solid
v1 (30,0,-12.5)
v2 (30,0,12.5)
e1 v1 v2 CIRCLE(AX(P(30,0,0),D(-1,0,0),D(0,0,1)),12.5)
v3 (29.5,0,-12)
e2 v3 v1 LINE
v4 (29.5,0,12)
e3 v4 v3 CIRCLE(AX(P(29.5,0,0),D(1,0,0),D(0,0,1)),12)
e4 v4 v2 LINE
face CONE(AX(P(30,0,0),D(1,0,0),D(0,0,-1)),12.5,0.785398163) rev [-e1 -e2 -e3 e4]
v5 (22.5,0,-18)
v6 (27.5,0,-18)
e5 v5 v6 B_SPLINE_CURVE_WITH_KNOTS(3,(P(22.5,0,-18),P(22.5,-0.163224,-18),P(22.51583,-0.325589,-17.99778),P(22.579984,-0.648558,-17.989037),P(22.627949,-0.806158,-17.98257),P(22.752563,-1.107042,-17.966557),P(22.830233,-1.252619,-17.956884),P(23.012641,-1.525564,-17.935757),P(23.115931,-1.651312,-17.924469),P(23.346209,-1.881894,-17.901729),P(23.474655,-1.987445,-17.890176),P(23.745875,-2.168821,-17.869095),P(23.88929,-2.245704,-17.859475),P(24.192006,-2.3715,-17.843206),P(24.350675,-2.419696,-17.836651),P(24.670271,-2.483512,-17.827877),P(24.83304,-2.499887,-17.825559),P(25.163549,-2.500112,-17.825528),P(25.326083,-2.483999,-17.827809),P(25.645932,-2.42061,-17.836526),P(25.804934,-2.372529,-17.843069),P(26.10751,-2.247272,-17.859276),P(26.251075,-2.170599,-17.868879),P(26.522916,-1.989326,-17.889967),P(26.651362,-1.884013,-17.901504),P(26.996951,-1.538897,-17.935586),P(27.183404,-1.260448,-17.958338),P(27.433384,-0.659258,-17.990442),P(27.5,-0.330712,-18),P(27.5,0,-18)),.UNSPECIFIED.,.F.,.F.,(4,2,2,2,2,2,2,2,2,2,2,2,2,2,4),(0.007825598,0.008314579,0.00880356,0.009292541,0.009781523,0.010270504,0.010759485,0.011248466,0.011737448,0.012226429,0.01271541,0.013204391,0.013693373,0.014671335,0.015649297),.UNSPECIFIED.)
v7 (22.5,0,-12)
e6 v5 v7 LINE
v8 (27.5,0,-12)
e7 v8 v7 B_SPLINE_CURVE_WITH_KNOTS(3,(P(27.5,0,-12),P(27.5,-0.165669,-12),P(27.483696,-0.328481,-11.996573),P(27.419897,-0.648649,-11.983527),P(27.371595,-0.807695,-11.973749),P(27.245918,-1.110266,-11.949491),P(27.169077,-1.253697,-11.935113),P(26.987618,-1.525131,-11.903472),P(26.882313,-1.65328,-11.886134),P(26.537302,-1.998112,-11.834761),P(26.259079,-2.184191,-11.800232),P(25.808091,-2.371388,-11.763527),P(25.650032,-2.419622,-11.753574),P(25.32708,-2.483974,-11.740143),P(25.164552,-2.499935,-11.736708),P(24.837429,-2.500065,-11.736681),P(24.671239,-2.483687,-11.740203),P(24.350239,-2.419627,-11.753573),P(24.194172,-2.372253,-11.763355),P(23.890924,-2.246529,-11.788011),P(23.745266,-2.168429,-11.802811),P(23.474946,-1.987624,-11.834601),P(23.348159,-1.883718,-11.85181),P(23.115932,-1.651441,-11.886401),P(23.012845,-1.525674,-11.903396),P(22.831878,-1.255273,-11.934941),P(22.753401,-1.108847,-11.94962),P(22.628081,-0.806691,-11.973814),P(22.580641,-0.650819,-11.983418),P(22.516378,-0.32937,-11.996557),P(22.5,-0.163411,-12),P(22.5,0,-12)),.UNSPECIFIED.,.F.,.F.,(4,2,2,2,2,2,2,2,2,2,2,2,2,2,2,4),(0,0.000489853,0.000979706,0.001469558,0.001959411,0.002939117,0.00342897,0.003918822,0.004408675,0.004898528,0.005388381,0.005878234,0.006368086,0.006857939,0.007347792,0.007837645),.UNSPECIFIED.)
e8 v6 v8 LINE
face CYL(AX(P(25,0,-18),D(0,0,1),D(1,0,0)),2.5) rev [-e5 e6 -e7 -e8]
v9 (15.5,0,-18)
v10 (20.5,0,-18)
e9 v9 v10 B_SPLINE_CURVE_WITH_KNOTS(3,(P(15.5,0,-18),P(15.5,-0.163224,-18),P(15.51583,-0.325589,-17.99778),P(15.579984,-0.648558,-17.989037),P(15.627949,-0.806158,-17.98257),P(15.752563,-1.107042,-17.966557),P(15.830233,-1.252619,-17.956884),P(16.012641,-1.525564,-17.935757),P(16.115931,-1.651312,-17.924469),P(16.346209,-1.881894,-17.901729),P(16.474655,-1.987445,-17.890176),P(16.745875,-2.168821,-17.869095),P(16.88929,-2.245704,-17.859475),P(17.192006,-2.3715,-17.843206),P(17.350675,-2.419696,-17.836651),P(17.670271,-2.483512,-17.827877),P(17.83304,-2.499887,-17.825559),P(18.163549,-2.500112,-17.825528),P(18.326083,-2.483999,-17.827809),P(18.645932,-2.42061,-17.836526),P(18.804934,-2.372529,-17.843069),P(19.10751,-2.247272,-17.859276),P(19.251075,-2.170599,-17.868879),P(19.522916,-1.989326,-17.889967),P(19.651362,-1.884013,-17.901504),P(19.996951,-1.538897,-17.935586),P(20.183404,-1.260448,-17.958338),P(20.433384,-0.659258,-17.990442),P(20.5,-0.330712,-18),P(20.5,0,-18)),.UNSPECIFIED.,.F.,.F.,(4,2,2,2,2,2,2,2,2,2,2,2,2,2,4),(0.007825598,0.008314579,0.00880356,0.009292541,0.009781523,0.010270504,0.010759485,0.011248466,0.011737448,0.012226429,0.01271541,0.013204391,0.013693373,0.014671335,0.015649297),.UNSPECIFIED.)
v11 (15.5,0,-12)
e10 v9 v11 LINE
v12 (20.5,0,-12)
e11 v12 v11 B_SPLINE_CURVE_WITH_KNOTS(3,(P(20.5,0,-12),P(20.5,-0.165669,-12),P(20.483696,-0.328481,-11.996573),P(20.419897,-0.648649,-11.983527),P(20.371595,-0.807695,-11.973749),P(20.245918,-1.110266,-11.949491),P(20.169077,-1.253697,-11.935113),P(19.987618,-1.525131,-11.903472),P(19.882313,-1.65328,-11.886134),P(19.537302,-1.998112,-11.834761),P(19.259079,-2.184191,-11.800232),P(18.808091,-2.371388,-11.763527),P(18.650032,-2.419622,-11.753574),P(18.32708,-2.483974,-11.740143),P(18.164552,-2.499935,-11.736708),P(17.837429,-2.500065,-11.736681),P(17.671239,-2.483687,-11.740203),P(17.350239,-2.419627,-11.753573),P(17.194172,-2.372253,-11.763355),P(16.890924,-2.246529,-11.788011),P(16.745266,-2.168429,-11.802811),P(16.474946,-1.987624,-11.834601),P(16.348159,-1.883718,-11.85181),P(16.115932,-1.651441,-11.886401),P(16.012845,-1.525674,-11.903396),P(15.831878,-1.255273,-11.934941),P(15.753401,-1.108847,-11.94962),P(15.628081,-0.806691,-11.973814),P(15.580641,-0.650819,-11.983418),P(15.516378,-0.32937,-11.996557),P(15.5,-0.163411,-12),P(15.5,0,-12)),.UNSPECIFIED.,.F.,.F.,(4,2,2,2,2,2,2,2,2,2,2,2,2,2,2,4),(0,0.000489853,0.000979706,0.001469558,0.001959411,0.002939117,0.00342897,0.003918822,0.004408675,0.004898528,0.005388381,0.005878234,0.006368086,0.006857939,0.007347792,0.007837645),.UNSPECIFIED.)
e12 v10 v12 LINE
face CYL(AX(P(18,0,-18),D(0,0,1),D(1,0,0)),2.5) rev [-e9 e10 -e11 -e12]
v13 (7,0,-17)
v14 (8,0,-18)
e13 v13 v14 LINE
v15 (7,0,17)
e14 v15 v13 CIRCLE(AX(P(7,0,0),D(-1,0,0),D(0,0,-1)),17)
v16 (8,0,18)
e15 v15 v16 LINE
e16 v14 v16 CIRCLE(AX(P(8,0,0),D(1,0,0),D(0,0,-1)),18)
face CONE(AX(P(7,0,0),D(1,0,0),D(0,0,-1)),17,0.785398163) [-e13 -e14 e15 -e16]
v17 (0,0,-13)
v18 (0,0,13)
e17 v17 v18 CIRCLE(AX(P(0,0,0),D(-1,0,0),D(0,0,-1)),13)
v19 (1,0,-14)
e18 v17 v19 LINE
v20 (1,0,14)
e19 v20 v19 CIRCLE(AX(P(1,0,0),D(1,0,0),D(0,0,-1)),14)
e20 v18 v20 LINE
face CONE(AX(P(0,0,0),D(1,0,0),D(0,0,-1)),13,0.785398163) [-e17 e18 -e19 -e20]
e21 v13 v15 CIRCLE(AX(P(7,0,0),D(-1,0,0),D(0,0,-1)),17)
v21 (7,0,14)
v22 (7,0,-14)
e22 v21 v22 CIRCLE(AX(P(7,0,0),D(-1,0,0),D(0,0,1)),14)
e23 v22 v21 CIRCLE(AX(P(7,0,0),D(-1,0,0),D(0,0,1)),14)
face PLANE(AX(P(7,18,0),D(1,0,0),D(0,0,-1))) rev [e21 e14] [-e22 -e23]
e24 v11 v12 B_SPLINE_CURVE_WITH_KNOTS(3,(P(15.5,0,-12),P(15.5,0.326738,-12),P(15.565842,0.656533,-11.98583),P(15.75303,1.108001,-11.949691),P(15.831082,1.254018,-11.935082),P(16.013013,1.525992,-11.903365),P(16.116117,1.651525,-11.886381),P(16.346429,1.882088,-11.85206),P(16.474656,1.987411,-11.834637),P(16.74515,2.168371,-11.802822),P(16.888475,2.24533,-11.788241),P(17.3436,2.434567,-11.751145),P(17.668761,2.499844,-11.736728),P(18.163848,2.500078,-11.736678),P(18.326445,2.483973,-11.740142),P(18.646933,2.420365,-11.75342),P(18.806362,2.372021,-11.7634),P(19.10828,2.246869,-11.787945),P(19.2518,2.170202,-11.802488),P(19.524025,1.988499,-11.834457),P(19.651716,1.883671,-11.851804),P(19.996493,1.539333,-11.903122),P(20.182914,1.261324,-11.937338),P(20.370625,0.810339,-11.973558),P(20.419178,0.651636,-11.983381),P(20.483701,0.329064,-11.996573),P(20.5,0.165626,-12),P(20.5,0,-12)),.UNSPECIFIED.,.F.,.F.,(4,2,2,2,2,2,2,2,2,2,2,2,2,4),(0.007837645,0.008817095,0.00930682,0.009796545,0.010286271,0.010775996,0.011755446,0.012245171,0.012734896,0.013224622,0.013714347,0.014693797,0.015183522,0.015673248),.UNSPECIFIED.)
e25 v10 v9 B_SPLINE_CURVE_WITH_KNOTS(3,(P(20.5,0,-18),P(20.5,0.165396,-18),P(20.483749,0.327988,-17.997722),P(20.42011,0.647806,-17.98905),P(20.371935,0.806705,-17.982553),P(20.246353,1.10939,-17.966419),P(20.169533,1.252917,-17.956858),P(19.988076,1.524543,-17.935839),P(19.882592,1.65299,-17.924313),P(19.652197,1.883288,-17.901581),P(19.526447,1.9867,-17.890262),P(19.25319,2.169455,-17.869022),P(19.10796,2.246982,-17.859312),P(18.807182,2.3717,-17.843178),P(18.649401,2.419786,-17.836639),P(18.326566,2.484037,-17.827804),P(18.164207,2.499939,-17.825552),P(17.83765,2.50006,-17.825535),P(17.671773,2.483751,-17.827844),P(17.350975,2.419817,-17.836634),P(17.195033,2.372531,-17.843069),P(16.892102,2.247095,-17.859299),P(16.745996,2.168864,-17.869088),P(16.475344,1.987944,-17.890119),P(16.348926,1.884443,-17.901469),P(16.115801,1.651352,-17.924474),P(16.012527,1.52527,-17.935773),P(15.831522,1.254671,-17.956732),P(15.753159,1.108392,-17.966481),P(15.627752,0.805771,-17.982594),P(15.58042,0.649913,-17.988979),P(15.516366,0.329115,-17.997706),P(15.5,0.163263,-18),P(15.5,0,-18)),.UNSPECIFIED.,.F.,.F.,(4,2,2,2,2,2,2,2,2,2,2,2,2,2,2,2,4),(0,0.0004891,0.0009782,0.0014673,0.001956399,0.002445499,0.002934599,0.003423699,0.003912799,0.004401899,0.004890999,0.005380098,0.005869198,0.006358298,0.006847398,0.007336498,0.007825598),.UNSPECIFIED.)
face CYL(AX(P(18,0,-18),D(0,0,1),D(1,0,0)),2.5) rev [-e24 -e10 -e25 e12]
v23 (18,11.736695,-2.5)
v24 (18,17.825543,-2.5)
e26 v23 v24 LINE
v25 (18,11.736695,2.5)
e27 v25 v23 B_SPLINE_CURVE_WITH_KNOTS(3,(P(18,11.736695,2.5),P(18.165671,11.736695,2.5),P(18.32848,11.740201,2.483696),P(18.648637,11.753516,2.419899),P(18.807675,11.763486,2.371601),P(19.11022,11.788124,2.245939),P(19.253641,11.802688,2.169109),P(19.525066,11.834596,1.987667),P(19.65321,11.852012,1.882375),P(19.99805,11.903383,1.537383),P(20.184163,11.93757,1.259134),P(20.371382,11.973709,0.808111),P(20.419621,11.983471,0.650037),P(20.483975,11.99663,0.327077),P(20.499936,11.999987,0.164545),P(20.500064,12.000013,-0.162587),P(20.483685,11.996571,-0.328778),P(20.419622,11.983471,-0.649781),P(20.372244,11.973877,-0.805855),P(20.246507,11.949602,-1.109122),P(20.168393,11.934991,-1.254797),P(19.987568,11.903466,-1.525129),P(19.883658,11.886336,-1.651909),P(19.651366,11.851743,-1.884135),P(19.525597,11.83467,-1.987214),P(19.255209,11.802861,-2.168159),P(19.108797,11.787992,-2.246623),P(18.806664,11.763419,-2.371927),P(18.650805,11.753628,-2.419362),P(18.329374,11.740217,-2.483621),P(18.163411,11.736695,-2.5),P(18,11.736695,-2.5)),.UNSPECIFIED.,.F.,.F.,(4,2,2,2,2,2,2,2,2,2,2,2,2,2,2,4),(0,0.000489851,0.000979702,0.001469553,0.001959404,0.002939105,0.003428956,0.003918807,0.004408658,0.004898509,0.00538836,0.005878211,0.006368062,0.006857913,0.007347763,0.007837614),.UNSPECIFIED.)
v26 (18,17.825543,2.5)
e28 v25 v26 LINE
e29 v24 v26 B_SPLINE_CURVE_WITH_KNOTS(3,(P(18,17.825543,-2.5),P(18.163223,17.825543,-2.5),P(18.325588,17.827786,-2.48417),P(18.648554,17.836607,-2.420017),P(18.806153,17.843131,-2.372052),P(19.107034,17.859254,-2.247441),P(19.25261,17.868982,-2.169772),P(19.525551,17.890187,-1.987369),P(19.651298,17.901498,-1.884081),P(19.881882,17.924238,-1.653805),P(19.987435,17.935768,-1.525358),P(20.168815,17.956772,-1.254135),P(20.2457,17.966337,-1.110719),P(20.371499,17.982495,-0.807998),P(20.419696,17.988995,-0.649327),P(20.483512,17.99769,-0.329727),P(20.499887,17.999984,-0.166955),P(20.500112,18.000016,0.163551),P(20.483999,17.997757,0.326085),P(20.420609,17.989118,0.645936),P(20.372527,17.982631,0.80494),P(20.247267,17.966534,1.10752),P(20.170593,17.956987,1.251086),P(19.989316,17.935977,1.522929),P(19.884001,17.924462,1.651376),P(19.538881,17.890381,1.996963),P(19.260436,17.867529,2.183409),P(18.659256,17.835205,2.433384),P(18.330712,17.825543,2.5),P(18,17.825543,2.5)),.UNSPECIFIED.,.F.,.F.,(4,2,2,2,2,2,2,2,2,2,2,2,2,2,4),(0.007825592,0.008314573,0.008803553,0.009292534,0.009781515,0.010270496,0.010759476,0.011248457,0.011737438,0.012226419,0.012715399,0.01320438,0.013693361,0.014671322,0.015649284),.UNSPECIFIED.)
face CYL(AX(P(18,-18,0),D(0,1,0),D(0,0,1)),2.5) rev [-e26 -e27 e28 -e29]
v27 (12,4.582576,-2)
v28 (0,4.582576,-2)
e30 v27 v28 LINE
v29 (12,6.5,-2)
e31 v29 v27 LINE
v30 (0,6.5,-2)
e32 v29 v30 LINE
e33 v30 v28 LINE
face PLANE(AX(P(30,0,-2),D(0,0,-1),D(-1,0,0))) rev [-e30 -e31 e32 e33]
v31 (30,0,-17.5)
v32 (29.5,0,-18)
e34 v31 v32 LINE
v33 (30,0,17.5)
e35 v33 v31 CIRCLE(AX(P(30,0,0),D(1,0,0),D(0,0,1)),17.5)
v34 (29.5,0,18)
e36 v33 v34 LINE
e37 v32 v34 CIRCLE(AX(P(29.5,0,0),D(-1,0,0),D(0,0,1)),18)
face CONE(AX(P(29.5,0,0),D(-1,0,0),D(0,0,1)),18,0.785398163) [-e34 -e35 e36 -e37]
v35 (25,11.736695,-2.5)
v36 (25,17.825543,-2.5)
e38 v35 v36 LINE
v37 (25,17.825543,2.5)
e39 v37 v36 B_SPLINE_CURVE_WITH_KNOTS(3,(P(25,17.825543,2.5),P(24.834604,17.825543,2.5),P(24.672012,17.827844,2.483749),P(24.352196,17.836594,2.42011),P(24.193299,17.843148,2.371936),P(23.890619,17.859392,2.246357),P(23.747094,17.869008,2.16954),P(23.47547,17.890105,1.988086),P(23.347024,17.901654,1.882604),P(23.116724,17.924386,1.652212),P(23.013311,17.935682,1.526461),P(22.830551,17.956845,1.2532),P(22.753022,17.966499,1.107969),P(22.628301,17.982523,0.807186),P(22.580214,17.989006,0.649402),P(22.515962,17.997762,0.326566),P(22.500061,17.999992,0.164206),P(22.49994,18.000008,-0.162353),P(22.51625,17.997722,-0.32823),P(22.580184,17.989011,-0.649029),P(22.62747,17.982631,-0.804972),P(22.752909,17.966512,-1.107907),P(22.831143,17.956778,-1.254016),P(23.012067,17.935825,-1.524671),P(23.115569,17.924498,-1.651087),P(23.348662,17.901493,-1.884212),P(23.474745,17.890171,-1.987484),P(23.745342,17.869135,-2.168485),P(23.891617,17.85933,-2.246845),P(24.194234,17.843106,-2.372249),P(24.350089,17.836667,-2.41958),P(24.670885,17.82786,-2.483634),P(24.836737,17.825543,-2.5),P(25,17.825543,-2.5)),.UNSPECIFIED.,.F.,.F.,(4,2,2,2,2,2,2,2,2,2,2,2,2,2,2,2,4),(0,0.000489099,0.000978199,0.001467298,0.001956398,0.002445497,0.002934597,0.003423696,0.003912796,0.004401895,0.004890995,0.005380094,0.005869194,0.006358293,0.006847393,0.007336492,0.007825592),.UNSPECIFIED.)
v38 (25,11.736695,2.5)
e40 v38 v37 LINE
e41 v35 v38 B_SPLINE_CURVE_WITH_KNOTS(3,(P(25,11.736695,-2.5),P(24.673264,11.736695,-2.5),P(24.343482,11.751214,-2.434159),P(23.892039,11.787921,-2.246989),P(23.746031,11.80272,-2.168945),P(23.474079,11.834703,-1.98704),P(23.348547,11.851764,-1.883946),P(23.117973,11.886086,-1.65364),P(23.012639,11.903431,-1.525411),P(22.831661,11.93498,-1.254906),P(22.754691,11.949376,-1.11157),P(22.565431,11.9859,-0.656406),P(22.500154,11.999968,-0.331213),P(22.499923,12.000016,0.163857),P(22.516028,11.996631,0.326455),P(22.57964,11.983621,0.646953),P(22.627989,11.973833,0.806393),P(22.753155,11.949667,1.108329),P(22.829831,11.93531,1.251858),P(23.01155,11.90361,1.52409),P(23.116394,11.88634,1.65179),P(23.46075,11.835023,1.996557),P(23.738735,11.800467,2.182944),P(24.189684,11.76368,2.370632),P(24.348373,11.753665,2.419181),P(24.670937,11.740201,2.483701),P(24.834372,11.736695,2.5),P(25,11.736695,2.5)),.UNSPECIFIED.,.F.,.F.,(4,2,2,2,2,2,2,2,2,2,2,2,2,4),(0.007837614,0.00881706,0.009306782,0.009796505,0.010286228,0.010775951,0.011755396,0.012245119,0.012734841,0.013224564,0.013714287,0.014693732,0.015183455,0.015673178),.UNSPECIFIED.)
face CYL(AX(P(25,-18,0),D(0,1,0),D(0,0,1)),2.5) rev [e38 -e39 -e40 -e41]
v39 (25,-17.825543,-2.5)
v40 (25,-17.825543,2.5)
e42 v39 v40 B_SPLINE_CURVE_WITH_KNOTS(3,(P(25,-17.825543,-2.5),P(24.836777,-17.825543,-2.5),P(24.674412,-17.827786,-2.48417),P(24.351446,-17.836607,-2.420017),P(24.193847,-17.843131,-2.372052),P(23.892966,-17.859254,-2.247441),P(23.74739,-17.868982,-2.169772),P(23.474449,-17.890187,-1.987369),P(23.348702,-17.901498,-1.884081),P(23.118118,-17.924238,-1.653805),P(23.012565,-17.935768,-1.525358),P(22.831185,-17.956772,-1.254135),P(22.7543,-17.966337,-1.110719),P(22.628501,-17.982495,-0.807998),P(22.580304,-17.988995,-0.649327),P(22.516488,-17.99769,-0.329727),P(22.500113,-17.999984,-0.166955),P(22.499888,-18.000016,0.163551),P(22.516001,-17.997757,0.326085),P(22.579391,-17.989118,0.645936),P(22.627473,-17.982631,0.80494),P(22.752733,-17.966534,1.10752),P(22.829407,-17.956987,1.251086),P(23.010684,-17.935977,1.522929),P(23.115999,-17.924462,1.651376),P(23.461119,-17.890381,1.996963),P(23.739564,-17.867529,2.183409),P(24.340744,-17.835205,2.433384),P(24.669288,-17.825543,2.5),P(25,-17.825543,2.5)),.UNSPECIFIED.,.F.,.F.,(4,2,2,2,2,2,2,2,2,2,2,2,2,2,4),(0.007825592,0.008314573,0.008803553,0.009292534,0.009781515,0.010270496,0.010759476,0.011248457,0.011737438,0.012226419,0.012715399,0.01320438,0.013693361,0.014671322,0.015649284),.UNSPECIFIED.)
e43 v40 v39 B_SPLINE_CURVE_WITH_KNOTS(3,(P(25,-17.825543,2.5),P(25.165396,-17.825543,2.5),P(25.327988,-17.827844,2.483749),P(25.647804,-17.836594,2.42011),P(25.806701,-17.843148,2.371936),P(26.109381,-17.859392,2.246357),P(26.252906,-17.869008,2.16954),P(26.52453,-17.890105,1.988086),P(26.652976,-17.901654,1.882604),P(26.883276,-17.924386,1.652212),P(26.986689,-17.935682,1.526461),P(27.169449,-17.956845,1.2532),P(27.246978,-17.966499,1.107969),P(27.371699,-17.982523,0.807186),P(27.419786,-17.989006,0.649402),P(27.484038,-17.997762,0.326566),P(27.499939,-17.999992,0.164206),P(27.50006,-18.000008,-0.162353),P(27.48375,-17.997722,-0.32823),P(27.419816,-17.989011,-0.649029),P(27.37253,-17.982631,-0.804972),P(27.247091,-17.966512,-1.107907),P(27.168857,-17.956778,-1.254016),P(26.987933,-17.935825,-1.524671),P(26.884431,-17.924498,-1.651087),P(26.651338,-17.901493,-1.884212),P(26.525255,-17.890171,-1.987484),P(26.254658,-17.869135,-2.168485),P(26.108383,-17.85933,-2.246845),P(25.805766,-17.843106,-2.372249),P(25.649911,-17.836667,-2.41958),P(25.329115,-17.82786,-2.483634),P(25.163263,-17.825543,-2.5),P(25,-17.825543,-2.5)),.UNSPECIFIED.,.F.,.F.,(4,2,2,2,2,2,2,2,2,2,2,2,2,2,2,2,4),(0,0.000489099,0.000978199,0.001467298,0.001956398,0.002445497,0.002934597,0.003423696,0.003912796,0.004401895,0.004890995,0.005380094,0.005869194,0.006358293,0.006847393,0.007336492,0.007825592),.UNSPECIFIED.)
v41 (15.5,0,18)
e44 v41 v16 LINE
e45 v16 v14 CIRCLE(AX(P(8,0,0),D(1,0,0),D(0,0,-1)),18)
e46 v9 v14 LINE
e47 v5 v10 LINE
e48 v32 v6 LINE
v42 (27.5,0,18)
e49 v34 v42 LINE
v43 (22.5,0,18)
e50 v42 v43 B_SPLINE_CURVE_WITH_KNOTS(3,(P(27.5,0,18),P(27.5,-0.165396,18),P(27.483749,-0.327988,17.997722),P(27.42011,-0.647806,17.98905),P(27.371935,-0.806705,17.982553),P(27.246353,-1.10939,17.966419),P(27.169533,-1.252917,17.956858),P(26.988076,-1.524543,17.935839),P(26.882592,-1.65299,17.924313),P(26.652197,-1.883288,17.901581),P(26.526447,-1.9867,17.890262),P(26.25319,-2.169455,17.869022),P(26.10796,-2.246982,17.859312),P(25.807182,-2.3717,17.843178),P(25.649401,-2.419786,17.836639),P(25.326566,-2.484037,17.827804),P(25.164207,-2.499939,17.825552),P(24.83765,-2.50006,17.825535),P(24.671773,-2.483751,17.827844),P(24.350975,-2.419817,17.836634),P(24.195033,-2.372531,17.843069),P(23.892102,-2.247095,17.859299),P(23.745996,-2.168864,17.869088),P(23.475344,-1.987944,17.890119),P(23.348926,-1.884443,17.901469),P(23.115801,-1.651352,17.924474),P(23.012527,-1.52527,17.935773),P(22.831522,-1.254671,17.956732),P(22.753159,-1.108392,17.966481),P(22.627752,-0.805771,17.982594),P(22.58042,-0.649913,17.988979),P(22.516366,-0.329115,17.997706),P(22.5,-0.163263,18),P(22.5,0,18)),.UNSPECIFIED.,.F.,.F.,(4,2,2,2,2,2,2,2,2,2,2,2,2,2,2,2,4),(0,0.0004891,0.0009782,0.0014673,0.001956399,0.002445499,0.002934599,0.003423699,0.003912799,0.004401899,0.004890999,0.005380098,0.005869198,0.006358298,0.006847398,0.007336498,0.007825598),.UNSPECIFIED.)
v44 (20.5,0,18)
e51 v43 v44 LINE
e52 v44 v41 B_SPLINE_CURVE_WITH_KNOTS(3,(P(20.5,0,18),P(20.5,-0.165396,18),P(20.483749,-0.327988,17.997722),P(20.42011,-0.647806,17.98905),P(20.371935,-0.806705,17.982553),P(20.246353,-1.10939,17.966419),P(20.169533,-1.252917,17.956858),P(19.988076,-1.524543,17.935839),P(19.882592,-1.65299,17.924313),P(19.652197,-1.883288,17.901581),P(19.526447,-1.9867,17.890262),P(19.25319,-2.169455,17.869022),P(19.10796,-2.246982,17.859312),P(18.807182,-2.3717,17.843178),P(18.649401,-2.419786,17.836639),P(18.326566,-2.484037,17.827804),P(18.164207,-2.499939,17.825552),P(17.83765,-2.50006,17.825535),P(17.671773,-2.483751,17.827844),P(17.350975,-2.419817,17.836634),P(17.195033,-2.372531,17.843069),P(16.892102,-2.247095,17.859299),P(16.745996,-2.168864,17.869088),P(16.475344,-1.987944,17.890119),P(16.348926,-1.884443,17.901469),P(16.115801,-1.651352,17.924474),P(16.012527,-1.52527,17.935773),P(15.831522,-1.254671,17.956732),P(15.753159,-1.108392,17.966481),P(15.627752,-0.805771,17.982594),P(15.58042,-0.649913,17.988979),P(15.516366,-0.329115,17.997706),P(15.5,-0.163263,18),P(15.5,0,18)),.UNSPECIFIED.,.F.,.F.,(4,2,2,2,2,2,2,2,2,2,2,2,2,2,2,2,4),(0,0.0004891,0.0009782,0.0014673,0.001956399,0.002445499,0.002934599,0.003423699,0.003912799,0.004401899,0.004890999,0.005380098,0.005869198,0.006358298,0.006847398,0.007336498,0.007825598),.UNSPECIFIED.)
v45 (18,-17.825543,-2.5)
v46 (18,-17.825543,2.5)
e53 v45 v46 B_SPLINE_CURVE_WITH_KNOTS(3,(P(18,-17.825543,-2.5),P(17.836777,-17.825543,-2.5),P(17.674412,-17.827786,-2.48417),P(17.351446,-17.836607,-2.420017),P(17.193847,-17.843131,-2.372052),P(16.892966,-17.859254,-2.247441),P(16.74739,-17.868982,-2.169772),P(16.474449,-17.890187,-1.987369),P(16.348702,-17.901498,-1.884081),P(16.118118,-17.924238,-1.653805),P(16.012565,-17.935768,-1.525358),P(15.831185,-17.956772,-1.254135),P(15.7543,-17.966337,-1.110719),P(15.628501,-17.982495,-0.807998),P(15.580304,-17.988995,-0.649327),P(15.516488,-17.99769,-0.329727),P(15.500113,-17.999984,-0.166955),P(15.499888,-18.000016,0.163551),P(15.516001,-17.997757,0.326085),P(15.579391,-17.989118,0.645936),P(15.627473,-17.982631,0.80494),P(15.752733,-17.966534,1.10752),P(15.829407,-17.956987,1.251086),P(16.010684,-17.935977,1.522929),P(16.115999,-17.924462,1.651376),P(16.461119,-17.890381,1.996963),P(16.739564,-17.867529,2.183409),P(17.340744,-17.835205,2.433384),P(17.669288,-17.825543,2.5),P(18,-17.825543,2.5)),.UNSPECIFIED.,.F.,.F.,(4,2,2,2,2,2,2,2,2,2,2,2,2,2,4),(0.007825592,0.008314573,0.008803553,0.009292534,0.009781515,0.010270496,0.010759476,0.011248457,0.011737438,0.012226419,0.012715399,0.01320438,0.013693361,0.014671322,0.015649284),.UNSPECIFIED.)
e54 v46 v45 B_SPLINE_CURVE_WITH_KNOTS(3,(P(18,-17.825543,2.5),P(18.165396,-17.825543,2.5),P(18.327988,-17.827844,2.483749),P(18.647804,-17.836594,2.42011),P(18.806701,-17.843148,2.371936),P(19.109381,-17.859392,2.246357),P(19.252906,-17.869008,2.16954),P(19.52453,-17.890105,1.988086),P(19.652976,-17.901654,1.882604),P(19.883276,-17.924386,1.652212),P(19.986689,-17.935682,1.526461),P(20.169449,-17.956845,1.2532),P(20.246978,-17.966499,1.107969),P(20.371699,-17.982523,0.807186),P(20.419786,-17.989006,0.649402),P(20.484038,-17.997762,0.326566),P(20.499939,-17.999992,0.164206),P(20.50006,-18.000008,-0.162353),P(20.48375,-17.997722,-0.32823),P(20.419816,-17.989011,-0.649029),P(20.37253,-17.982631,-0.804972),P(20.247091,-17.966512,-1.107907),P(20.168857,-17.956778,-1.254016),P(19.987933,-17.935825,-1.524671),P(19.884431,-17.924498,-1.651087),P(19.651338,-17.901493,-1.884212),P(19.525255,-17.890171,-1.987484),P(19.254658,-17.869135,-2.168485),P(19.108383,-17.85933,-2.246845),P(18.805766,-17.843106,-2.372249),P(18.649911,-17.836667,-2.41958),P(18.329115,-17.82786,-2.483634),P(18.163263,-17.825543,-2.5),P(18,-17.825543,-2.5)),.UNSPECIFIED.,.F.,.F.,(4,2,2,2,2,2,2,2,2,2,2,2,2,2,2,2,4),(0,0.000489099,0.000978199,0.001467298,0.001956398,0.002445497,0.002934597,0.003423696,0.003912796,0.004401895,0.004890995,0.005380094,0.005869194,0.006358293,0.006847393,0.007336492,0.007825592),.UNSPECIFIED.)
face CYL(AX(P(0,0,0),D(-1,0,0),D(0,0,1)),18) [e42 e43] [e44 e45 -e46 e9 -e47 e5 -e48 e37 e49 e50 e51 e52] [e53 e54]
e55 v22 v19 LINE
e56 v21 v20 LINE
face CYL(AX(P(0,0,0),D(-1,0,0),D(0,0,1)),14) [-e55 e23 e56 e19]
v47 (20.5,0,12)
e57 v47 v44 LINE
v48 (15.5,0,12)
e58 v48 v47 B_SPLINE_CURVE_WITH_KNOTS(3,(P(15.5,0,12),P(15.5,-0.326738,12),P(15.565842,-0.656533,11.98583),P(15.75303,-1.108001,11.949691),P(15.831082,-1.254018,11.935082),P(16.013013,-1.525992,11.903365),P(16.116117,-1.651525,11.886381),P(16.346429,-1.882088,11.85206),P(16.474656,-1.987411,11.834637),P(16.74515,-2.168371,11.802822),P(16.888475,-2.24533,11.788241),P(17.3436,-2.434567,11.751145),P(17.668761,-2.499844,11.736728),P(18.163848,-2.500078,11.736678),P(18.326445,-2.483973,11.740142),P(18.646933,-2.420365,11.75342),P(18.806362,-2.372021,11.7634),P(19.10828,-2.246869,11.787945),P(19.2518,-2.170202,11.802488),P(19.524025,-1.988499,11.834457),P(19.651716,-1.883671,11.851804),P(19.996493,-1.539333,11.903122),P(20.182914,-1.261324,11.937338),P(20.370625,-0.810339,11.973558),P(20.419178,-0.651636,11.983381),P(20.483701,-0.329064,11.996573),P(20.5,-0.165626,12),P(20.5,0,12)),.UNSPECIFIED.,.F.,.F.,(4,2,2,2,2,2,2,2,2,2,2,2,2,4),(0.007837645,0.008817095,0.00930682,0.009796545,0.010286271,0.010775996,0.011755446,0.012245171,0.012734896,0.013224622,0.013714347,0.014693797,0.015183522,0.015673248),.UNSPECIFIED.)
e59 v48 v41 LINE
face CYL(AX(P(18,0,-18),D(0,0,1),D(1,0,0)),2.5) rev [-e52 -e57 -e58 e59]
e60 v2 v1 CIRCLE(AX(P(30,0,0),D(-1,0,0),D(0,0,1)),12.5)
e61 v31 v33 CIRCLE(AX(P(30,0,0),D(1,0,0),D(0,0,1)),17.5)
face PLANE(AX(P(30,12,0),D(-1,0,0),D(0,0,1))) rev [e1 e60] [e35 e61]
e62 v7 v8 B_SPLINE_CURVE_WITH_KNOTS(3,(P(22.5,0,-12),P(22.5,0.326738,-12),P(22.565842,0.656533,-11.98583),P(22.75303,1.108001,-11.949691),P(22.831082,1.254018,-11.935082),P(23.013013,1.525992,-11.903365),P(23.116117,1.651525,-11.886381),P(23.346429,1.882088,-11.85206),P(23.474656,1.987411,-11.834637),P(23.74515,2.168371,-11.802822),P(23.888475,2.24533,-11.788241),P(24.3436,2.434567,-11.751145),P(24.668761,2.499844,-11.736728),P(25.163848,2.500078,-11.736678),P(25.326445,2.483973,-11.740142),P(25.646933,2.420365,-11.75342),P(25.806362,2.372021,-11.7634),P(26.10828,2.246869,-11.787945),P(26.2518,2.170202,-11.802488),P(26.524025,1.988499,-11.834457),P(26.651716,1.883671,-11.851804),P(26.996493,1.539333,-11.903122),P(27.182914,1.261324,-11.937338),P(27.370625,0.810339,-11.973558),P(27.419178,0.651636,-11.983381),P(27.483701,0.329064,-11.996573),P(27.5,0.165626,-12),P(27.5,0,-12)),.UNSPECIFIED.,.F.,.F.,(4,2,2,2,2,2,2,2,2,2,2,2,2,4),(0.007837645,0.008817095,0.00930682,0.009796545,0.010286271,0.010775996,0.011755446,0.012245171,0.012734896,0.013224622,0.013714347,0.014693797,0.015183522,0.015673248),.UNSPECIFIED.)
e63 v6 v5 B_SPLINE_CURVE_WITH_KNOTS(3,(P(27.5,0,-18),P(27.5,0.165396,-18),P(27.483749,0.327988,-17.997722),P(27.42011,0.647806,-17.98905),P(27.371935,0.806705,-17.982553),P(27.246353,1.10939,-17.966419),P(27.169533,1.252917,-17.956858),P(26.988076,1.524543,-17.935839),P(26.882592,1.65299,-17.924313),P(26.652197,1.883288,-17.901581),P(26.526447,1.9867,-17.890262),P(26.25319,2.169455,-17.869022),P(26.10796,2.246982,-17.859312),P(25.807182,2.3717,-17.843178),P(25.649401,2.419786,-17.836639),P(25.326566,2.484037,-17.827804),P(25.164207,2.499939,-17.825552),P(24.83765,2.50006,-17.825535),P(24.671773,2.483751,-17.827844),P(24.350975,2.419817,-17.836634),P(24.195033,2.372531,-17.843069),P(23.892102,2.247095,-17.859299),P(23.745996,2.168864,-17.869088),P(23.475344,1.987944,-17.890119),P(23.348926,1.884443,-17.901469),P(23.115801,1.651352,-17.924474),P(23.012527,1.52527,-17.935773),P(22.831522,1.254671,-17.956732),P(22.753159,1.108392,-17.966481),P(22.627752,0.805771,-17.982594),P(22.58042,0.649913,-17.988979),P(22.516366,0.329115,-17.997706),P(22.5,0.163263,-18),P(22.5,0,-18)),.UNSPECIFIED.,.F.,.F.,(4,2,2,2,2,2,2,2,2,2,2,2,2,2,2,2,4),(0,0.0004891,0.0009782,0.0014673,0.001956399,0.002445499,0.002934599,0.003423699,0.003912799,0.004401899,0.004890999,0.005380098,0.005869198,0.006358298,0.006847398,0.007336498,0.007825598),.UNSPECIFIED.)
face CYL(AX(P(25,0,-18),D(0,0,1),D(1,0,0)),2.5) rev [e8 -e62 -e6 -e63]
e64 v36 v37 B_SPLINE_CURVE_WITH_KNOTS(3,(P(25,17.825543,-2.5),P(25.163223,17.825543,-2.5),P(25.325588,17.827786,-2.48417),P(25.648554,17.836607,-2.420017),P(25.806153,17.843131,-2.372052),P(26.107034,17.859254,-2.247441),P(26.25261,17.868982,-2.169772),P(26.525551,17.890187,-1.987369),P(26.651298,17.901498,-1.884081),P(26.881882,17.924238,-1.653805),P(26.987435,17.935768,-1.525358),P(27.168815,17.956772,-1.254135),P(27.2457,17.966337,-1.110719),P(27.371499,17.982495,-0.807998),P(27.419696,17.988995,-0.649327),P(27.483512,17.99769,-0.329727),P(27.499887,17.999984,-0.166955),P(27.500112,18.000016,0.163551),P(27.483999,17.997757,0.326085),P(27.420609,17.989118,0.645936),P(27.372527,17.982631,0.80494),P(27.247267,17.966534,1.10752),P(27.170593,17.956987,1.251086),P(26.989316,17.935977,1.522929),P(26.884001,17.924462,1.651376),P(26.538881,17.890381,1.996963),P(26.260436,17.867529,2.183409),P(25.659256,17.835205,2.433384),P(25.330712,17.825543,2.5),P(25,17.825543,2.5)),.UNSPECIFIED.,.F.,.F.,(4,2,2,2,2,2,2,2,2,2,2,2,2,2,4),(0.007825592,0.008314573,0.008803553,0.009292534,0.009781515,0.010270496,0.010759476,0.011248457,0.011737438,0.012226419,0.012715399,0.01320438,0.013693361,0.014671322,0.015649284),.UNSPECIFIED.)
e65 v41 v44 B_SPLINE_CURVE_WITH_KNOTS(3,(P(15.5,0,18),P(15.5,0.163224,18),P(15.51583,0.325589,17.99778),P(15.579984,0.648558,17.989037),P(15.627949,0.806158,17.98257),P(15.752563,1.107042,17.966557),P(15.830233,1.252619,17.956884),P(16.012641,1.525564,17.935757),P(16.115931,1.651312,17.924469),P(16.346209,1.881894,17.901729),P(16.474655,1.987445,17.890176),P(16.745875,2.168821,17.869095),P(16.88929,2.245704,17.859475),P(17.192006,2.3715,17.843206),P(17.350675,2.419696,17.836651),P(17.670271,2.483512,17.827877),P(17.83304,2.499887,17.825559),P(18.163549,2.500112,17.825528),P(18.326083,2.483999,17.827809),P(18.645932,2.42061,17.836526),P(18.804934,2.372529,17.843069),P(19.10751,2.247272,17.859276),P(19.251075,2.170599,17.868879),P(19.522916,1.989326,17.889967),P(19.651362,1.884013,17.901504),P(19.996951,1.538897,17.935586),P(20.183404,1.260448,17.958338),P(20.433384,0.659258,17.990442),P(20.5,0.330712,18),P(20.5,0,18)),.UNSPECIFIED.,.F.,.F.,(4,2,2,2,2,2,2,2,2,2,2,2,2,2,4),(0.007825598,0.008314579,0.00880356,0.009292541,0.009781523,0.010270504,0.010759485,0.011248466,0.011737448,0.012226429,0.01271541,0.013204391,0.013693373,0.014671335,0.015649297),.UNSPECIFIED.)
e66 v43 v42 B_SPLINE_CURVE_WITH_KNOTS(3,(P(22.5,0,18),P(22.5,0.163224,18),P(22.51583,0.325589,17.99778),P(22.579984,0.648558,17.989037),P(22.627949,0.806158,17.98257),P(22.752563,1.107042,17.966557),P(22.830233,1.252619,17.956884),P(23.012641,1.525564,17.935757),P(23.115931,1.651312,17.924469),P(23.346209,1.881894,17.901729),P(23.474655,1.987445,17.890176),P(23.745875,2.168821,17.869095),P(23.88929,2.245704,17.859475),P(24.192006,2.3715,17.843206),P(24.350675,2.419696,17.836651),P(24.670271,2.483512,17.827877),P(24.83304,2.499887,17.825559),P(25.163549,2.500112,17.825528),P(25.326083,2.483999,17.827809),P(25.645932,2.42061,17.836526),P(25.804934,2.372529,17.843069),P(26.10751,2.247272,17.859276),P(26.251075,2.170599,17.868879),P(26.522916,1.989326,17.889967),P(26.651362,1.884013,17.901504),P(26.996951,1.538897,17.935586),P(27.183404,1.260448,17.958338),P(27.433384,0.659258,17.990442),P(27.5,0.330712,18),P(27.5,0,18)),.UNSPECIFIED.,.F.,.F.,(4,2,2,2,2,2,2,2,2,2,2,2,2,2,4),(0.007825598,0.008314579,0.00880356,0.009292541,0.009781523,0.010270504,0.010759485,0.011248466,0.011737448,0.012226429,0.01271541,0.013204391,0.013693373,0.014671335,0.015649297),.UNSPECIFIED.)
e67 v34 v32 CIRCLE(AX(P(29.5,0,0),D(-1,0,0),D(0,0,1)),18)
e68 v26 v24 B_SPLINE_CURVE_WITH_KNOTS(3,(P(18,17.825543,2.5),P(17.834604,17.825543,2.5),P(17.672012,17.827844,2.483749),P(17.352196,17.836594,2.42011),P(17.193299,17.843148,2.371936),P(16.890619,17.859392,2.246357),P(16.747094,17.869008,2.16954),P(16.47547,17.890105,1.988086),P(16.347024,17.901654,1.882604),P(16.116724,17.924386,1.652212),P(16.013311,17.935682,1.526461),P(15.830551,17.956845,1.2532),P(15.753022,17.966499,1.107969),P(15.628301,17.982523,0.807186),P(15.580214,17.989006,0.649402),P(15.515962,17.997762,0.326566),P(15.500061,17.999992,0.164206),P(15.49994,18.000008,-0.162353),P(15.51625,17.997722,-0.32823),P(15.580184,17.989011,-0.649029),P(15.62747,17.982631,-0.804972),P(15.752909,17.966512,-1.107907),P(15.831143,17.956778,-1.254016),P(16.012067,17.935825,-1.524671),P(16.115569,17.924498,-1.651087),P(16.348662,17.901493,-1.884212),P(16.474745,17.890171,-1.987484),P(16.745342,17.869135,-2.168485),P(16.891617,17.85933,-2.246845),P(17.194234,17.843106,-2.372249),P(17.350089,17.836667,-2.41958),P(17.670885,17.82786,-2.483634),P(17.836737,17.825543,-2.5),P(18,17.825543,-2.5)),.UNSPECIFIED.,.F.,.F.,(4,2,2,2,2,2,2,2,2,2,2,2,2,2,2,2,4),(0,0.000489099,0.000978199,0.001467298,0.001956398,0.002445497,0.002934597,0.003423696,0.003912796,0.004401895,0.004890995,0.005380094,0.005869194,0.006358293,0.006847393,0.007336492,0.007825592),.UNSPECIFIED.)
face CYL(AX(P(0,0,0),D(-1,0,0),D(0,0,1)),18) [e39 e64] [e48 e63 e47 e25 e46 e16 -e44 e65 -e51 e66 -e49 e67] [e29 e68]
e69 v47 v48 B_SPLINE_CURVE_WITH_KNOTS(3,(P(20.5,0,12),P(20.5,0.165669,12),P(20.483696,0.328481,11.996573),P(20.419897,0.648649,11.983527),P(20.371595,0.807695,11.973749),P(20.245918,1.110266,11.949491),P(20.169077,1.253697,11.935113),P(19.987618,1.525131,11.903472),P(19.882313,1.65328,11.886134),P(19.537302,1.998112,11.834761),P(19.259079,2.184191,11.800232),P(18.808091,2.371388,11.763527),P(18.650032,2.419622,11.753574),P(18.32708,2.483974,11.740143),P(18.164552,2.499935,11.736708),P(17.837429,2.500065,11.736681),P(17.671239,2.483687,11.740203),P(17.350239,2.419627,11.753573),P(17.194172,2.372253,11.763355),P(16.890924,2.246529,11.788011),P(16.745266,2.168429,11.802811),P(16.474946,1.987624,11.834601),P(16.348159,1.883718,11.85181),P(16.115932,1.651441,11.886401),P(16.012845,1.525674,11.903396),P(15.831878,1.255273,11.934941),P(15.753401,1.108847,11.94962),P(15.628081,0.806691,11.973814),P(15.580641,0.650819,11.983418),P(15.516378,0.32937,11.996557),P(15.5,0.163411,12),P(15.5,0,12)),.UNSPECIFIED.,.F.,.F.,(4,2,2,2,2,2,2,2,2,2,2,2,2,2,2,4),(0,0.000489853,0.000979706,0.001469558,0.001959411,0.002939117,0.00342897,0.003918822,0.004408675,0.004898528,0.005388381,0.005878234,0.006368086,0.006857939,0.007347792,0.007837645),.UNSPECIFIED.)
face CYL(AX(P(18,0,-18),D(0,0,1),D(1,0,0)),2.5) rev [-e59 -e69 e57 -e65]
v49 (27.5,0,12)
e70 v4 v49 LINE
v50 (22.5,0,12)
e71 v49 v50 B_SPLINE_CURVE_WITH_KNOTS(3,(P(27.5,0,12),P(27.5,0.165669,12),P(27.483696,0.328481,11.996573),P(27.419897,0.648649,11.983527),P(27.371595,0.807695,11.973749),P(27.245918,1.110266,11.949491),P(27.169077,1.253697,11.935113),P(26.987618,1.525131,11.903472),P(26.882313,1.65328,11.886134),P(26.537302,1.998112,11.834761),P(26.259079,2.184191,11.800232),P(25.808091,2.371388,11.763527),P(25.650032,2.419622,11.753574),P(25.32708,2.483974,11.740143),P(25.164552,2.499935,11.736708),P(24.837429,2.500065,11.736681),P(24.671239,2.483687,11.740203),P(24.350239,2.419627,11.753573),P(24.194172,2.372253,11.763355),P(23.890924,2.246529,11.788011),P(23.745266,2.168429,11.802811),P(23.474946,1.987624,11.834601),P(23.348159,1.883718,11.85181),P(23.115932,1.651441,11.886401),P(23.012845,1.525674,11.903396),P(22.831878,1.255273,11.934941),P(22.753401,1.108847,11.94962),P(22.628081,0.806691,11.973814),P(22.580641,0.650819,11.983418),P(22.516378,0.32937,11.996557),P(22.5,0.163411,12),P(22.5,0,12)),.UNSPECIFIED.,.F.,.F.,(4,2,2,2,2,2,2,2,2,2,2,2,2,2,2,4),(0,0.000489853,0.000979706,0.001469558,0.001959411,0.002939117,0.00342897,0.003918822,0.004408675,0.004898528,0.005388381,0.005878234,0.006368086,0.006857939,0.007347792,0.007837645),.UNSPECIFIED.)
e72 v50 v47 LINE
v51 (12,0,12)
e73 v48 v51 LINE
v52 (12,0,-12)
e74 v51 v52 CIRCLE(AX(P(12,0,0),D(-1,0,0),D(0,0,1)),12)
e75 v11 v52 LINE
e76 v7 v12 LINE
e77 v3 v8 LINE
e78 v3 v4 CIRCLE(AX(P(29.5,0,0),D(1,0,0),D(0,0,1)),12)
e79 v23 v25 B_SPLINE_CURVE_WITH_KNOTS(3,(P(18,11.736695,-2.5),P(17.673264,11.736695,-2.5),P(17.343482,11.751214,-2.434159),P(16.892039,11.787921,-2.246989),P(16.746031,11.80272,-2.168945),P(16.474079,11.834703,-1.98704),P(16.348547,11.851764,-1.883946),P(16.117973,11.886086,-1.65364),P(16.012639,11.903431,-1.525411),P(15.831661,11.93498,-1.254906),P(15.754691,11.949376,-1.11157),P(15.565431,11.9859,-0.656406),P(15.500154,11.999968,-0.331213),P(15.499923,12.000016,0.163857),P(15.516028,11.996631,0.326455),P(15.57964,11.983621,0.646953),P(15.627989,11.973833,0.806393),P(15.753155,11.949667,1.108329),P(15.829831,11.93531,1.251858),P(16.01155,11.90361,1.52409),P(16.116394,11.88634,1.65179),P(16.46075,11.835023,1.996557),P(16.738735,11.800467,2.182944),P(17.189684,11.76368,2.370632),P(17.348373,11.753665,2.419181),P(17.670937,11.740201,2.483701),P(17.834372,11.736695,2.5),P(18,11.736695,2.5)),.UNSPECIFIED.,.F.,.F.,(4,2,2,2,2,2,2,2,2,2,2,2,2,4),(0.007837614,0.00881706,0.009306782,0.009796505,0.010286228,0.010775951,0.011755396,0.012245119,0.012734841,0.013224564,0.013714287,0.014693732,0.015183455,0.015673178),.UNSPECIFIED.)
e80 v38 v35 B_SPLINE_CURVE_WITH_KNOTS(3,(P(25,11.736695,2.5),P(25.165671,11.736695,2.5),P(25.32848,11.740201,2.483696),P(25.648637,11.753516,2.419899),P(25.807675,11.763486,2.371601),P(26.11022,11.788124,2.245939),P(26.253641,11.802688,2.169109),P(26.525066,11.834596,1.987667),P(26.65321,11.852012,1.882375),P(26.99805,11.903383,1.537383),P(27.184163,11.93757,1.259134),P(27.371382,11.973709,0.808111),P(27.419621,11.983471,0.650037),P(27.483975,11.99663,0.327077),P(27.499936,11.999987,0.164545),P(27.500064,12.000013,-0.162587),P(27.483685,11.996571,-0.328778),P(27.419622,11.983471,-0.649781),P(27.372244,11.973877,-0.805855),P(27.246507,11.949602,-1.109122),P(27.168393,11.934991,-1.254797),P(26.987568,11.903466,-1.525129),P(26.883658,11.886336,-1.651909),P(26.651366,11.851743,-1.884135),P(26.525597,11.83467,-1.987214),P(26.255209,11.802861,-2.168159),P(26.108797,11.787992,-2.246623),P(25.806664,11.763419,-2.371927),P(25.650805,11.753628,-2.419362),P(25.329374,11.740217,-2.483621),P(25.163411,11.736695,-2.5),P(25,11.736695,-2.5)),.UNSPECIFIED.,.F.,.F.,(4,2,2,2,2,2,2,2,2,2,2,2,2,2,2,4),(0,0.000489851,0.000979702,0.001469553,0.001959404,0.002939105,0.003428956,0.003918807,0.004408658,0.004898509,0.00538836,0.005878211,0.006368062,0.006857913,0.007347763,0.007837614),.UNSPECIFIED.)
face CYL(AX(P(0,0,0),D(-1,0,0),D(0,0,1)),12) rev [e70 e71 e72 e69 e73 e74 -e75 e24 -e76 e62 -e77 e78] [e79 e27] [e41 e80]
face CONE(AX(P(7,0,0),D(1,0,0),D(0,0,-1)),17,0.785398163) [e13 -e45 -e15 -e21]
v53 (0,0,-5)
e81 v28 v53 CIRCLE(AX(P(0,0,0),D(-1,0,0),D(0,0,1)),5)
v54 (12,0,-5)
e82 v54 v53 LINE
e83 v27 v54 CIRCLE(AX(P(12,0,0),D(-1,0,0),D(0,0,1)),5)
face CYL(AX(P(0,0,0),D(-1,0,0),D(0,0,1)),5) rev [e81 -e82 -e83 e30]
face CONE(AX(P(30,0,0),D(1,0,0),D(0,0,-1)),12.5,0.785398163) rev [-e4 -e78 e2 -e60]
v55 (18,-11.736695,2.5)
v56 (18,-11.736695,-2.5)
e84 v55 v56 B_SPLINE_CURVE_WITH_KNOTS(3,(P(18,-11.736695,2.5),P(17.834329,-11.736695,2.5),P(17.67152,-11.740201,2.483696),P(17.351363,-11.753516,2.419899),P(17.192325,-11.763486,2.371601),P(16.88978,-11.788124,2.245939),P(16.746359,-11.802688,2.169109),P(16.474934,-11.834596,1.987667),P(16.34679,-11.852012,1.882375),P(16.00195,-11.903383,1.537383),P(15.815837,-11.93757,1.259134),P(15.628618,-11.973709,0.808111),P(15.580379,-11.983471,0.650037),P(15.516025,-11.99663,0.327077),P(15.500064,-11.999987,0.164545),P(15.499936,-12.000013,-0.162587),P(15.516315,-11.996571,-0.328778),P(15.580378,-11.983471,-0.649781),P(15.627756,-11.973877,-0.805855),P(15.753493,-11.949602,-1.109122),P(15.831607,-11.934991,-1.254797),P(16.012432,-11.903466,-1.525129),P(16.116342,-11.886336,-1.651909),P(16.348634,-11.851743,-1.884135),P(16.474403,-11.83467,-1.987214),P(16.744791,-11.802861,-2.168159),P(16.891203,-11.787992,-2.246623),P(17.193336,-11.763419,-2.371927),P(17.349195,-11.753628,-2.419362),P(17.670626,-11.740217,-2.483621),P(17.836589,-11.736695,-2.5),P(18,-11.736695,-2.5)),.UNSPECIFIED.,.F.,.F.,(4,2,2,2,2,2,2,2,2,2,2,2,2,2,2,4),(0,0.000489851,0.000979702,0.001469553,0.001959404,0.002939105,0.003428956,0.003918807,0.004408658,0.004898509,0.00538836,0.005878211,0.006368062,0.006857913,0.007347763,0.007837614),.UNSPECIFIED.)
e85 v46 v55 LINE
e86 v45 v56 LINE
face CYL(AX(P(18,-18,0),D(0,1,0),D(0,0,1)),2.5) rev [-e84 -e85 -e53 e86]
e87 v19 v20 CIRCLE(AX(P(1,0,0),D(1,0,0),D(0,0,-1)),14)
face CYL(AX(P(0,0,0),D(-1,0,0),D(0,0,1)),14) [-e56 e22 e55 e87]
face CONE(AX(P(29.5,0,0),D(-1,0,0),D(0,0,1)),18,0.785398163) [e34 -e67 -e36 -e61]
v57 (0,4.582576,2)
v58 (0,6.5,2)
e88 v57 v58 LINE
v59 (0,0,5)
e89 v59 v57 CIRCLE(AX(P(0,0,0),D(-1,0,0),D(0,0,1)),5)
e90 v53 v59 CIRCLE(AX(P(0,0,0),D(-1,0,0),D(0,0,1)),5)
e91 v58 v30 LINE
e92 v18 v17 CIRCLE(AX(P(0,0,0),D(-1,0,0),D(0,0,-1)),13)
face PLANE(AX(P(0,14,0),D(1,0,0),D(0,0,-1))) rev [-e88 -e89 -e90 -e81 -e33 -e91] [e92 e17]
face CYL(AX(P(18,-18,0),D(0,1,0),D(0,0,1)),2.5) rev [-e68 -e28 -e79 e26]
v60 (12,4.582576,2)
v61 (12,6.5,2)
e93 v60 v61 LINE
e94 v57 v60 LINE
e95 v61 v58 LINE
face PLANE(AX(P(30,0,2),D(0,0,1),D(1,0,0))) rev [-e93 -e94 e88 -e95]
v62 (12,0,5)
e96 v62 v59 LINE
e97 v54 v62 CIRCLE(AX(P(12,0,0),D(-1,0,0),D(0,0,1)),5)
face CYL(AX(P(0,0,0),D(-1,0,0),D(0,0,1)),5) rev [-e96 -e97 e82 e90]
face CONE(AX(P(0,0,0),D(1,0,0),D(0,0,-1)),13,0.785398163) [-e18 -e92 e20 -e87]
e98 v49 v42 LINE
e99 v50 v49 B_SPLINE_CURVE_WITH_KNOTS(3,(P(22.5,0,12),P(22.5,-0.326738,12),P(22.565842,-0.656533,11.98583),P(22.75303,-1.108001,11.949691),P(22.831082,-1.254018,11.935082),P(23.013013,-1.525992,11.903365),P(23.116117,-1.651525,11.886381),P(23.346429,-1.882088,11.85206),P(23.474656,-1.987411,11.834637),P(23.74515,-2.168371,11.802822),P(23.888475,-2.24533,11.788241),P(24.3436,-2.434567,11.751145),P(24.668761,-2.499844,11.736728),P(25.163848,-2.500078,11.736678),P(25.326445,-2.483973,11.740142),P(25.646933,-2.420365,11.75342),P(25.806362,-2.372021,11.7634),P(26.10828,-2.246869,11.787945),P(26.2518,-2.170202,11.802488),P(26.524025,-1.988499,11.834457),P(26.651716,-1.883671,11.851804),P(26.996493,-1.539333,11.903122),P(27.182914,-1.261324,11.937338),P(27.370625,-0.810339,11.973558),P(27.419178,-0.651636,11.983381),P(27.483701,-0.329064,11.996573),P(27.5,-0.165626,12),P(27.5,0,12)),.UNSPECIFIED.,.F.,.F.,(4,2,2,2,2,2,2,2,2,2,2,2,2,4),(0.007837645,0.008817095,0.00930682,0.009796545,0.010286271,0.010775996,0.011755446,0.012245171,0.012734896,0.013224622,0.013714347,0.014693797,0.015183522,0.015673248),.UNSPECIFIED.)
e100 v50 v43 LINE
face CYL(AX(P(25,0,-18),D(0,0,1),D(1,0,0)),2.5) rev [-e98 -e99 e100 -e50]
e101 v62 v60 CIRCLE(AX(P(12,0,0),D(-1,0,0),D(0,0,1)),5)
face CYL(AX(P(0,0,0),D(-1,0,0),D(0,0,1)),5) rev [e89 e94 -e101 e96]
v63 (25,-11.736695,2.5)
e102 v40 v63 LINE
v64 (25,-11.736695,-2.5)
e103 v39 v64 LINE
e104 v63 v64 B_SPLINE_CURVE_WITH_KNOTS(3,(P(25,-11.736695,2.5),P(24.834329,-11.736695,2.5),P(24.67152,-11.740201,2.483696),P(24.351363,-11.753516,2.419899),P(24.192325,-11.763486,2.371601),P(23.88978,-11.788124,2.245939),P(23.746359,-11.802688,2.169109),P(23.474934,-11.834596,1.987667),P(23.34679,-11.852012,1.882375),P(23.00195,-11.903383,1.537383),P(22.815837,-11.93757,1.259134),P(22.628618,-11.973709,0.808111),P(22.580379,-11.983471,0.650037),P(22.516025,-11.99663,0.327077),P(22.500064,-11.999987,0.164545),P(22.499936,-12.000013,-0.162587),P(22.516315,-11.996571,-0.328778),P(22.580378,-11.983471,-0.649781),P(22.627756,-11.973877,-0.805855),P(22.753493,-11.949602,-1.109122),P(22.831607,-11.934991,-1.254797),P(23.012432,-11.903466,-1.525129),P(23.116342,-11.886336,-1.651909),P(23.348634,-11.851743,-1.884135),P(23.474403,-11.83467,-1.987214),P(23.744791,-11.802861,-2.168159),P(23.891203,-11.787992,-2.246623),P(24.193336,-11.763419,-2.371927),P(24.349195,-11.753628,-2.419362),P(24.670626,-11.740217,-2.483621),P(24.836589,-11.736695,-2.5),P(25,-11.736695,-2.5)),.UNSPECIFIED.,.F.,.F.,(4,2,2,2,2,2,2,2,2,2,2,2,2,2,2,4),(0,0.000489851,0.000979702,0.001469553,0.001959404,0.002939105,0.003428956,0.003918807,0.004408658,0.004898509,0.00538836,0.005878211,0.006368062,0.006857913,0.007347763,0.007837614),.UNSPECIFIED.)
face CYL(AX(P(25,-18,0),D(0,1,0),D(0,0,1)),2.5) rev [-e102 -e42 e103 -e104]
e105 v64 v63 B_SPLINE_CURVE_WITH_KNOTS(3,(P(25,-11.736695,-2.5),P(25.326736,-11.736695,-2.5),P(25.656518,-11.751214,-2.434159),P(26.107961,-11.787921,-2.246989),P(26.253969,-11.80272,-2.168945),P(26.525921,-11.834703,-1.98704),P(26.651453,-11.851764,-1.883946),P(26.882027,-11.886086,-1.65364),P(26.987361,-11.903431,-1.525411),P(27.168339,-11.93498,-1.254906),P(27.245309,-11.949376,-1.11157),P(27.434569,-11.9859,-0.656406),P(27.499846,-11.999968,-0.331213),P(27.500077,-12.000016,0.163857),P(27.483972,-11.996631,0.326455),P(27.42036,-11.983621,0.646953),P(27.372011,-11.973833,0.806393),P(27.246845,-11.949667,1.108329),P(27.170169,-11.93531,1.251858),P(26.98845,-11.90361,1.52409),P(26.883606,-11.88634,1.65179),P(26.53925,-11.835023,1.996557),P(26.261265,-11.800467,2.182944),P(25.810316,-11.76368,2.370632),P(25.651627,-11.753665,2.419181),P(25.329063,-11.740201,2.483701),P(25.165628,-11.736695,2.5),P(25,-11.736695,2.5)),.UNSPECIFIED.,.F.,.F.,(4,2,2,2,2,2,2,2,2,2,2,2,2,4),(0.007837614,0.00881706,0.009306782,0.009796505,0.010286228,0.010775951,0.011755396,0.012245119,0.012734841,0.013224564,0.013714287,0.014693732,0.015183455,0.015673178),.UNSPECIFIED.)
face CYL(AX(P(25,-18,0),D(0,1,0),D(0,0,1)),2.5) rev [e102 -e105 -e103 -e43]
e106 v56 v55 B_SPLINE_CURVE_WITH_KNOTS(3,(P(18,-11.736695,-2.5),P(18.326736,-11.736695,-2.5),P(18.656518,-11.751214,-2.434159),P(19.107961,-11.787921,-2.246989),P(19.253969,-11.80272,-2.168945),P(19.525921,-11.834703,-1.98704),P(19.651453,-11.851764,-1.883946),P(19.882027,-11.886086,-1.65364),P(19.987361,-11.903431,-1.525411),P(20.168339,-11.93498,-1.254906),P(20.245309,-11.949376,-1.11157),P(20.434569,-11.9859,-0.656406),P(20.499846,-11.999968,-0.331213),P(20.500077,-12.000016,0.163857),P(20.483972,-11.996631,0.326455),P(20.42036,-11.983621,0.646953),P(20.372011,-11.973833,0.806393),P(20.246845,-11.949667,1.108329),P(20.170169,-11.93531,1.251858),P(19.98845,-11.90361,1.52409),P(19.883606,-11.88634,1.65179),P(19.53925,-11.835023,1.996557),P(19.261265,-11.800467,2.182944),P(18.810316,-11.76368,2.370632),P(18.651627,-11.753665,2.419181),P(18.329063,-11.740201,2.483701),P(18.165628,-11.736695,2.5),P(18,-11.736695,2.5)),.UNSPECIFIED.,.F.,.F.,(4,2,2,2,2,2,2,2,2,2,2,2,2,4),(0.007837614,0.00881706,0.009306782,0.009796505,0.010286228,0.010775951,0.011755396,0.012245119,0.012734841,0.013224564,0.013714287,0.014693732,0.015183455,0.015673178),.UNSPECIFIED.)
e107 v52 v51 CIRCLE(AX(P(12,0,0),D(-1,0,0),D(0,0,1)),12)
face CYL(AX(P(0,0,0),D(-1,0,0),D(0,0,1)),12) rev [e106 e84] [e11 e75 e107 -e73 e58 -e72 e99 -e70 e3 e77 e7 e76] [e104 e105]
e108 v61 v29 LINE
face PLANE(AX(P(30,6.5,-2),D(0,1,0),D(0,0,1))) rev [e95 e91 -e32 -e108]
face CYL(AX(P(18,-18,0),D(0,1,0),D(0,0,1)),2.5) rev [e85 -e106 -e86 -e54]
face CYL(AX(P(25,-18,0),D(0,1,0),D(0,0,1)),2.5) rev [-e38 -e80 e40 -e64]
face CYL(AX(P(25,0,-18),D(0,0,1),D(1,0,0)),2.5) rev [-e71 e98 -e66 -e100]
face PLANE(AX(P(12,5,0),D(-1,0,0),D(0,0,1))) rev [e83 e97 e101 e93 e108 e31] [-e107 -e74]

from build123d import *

# Parameters (mm, degrees)
SKETCH_2_W               = 4
SKETCH_2_H               = 6.5
CUT_EXTRUDE_1_DEPTH      = 40.344631146
CUT_EXTRUDE_2_DEPTH      = 40.344631146
CUT_EXTRUDE_2_DEPTH_BACK = 40.344631146
SKETCH_3_R               = 2.5
CHAMFER_1_SIZE           = 1
CHAMFER_2_SIZE           = 0.5
CUT_EXTRUDE_3_DEPTH      = 40.344631238
CUT_EXTRUDE_3_DEPTH_BACK = 40.344631238
SKETCH_4_R               = 2.5


with BuildPart() as part:
    # 草图1 → 旋转1 (revolve)
    with BuildSketch(Plane.XY, mode=Mode.PRIVATE) as revolve_1_sk:
        Polygon((0, 5), (12, 5), (12, 12), (30, 12), (30, 18), (7, 18), (7, 14), (0, 14), align=None)
    revolve(revolve_1_sk.sketch.rotate(Axis((0, 0, 0), (1, 0, 0)), 90), axis=Axis((0, 0, 0), (1, 0, 0)))

    # 草图2 → 切除-拉伸1 (cut, through all)
    with BuildSketch(Plane.ZY):
        with Locations((0, 3.25)):
            Rectangle(SKETCH_2_W, SKETCH_2_H)
    extrude(amount=-CUT_EXTRUDE_1_DEPTH, mode=Mode.SUBTRACT)

    # 草图3 → 切除-拉伸2 (cut, two sides: drawn at the far end of the back side and taken through both)
    with BuildSketch(Plane(origin=(0, 0, 0), x_dir=(1, 0, 0), z_dir=(0, 1, 0)).offset(-CUT_EXTRUDE_2_DEPTH_BACK)):
        with Locations(Location((18, 0, 0), (0, 0, 270))):
            Circle(SKETCH_3_R)
        with Locations(Location((25, 0, 0), (0, 0, 270))):
            Circle(SKETCH_3_R)
    extrude(amount=CUT_EXTRUDE_2_DEPTH + CUT_EXTRUDE_2_DEPTH_BACK, mode=Mode.SUBTRACT)

    # 倒角1
    chamfer_1_edges = [part.edges().sort_by_distance(p)[0] for p in [
        (0, 0, -14),
        (7, 0, -18),
    ]]
    chamfer(chamfer_1_edges, length=CHAMFER_1_SIZE)

    # 倒角2
    chamfer_2_edges = [part.edges().sort_by_distance(p)[0] for p in [
        (30, 0, -18),
        (30, 0, -12),
    ]]
    chamfer(chamfer_2_edges, length=CHAMFER_2_SIZE)

    # 草图4 → 切除-拉伸3 (cut, two sides: drawn at the far end of the back side and taken through both)
    with BuildSketch(Plane.XY.offset(-CUT_EXTRUDE_3_DEPTH_BACK)):
        with Locations((25, 0)):
            Circle(SKETCH_4_R)
        with Locations((18, 0)):
            Circle(SKETCH_4_R)
    extrude(amount=CUT_EXTRUDE_3_DEPTH + CUT_EXTRUDE_3_DEPTH_BACK, mode=Mode.SUBTRACT)


solid = part.part
